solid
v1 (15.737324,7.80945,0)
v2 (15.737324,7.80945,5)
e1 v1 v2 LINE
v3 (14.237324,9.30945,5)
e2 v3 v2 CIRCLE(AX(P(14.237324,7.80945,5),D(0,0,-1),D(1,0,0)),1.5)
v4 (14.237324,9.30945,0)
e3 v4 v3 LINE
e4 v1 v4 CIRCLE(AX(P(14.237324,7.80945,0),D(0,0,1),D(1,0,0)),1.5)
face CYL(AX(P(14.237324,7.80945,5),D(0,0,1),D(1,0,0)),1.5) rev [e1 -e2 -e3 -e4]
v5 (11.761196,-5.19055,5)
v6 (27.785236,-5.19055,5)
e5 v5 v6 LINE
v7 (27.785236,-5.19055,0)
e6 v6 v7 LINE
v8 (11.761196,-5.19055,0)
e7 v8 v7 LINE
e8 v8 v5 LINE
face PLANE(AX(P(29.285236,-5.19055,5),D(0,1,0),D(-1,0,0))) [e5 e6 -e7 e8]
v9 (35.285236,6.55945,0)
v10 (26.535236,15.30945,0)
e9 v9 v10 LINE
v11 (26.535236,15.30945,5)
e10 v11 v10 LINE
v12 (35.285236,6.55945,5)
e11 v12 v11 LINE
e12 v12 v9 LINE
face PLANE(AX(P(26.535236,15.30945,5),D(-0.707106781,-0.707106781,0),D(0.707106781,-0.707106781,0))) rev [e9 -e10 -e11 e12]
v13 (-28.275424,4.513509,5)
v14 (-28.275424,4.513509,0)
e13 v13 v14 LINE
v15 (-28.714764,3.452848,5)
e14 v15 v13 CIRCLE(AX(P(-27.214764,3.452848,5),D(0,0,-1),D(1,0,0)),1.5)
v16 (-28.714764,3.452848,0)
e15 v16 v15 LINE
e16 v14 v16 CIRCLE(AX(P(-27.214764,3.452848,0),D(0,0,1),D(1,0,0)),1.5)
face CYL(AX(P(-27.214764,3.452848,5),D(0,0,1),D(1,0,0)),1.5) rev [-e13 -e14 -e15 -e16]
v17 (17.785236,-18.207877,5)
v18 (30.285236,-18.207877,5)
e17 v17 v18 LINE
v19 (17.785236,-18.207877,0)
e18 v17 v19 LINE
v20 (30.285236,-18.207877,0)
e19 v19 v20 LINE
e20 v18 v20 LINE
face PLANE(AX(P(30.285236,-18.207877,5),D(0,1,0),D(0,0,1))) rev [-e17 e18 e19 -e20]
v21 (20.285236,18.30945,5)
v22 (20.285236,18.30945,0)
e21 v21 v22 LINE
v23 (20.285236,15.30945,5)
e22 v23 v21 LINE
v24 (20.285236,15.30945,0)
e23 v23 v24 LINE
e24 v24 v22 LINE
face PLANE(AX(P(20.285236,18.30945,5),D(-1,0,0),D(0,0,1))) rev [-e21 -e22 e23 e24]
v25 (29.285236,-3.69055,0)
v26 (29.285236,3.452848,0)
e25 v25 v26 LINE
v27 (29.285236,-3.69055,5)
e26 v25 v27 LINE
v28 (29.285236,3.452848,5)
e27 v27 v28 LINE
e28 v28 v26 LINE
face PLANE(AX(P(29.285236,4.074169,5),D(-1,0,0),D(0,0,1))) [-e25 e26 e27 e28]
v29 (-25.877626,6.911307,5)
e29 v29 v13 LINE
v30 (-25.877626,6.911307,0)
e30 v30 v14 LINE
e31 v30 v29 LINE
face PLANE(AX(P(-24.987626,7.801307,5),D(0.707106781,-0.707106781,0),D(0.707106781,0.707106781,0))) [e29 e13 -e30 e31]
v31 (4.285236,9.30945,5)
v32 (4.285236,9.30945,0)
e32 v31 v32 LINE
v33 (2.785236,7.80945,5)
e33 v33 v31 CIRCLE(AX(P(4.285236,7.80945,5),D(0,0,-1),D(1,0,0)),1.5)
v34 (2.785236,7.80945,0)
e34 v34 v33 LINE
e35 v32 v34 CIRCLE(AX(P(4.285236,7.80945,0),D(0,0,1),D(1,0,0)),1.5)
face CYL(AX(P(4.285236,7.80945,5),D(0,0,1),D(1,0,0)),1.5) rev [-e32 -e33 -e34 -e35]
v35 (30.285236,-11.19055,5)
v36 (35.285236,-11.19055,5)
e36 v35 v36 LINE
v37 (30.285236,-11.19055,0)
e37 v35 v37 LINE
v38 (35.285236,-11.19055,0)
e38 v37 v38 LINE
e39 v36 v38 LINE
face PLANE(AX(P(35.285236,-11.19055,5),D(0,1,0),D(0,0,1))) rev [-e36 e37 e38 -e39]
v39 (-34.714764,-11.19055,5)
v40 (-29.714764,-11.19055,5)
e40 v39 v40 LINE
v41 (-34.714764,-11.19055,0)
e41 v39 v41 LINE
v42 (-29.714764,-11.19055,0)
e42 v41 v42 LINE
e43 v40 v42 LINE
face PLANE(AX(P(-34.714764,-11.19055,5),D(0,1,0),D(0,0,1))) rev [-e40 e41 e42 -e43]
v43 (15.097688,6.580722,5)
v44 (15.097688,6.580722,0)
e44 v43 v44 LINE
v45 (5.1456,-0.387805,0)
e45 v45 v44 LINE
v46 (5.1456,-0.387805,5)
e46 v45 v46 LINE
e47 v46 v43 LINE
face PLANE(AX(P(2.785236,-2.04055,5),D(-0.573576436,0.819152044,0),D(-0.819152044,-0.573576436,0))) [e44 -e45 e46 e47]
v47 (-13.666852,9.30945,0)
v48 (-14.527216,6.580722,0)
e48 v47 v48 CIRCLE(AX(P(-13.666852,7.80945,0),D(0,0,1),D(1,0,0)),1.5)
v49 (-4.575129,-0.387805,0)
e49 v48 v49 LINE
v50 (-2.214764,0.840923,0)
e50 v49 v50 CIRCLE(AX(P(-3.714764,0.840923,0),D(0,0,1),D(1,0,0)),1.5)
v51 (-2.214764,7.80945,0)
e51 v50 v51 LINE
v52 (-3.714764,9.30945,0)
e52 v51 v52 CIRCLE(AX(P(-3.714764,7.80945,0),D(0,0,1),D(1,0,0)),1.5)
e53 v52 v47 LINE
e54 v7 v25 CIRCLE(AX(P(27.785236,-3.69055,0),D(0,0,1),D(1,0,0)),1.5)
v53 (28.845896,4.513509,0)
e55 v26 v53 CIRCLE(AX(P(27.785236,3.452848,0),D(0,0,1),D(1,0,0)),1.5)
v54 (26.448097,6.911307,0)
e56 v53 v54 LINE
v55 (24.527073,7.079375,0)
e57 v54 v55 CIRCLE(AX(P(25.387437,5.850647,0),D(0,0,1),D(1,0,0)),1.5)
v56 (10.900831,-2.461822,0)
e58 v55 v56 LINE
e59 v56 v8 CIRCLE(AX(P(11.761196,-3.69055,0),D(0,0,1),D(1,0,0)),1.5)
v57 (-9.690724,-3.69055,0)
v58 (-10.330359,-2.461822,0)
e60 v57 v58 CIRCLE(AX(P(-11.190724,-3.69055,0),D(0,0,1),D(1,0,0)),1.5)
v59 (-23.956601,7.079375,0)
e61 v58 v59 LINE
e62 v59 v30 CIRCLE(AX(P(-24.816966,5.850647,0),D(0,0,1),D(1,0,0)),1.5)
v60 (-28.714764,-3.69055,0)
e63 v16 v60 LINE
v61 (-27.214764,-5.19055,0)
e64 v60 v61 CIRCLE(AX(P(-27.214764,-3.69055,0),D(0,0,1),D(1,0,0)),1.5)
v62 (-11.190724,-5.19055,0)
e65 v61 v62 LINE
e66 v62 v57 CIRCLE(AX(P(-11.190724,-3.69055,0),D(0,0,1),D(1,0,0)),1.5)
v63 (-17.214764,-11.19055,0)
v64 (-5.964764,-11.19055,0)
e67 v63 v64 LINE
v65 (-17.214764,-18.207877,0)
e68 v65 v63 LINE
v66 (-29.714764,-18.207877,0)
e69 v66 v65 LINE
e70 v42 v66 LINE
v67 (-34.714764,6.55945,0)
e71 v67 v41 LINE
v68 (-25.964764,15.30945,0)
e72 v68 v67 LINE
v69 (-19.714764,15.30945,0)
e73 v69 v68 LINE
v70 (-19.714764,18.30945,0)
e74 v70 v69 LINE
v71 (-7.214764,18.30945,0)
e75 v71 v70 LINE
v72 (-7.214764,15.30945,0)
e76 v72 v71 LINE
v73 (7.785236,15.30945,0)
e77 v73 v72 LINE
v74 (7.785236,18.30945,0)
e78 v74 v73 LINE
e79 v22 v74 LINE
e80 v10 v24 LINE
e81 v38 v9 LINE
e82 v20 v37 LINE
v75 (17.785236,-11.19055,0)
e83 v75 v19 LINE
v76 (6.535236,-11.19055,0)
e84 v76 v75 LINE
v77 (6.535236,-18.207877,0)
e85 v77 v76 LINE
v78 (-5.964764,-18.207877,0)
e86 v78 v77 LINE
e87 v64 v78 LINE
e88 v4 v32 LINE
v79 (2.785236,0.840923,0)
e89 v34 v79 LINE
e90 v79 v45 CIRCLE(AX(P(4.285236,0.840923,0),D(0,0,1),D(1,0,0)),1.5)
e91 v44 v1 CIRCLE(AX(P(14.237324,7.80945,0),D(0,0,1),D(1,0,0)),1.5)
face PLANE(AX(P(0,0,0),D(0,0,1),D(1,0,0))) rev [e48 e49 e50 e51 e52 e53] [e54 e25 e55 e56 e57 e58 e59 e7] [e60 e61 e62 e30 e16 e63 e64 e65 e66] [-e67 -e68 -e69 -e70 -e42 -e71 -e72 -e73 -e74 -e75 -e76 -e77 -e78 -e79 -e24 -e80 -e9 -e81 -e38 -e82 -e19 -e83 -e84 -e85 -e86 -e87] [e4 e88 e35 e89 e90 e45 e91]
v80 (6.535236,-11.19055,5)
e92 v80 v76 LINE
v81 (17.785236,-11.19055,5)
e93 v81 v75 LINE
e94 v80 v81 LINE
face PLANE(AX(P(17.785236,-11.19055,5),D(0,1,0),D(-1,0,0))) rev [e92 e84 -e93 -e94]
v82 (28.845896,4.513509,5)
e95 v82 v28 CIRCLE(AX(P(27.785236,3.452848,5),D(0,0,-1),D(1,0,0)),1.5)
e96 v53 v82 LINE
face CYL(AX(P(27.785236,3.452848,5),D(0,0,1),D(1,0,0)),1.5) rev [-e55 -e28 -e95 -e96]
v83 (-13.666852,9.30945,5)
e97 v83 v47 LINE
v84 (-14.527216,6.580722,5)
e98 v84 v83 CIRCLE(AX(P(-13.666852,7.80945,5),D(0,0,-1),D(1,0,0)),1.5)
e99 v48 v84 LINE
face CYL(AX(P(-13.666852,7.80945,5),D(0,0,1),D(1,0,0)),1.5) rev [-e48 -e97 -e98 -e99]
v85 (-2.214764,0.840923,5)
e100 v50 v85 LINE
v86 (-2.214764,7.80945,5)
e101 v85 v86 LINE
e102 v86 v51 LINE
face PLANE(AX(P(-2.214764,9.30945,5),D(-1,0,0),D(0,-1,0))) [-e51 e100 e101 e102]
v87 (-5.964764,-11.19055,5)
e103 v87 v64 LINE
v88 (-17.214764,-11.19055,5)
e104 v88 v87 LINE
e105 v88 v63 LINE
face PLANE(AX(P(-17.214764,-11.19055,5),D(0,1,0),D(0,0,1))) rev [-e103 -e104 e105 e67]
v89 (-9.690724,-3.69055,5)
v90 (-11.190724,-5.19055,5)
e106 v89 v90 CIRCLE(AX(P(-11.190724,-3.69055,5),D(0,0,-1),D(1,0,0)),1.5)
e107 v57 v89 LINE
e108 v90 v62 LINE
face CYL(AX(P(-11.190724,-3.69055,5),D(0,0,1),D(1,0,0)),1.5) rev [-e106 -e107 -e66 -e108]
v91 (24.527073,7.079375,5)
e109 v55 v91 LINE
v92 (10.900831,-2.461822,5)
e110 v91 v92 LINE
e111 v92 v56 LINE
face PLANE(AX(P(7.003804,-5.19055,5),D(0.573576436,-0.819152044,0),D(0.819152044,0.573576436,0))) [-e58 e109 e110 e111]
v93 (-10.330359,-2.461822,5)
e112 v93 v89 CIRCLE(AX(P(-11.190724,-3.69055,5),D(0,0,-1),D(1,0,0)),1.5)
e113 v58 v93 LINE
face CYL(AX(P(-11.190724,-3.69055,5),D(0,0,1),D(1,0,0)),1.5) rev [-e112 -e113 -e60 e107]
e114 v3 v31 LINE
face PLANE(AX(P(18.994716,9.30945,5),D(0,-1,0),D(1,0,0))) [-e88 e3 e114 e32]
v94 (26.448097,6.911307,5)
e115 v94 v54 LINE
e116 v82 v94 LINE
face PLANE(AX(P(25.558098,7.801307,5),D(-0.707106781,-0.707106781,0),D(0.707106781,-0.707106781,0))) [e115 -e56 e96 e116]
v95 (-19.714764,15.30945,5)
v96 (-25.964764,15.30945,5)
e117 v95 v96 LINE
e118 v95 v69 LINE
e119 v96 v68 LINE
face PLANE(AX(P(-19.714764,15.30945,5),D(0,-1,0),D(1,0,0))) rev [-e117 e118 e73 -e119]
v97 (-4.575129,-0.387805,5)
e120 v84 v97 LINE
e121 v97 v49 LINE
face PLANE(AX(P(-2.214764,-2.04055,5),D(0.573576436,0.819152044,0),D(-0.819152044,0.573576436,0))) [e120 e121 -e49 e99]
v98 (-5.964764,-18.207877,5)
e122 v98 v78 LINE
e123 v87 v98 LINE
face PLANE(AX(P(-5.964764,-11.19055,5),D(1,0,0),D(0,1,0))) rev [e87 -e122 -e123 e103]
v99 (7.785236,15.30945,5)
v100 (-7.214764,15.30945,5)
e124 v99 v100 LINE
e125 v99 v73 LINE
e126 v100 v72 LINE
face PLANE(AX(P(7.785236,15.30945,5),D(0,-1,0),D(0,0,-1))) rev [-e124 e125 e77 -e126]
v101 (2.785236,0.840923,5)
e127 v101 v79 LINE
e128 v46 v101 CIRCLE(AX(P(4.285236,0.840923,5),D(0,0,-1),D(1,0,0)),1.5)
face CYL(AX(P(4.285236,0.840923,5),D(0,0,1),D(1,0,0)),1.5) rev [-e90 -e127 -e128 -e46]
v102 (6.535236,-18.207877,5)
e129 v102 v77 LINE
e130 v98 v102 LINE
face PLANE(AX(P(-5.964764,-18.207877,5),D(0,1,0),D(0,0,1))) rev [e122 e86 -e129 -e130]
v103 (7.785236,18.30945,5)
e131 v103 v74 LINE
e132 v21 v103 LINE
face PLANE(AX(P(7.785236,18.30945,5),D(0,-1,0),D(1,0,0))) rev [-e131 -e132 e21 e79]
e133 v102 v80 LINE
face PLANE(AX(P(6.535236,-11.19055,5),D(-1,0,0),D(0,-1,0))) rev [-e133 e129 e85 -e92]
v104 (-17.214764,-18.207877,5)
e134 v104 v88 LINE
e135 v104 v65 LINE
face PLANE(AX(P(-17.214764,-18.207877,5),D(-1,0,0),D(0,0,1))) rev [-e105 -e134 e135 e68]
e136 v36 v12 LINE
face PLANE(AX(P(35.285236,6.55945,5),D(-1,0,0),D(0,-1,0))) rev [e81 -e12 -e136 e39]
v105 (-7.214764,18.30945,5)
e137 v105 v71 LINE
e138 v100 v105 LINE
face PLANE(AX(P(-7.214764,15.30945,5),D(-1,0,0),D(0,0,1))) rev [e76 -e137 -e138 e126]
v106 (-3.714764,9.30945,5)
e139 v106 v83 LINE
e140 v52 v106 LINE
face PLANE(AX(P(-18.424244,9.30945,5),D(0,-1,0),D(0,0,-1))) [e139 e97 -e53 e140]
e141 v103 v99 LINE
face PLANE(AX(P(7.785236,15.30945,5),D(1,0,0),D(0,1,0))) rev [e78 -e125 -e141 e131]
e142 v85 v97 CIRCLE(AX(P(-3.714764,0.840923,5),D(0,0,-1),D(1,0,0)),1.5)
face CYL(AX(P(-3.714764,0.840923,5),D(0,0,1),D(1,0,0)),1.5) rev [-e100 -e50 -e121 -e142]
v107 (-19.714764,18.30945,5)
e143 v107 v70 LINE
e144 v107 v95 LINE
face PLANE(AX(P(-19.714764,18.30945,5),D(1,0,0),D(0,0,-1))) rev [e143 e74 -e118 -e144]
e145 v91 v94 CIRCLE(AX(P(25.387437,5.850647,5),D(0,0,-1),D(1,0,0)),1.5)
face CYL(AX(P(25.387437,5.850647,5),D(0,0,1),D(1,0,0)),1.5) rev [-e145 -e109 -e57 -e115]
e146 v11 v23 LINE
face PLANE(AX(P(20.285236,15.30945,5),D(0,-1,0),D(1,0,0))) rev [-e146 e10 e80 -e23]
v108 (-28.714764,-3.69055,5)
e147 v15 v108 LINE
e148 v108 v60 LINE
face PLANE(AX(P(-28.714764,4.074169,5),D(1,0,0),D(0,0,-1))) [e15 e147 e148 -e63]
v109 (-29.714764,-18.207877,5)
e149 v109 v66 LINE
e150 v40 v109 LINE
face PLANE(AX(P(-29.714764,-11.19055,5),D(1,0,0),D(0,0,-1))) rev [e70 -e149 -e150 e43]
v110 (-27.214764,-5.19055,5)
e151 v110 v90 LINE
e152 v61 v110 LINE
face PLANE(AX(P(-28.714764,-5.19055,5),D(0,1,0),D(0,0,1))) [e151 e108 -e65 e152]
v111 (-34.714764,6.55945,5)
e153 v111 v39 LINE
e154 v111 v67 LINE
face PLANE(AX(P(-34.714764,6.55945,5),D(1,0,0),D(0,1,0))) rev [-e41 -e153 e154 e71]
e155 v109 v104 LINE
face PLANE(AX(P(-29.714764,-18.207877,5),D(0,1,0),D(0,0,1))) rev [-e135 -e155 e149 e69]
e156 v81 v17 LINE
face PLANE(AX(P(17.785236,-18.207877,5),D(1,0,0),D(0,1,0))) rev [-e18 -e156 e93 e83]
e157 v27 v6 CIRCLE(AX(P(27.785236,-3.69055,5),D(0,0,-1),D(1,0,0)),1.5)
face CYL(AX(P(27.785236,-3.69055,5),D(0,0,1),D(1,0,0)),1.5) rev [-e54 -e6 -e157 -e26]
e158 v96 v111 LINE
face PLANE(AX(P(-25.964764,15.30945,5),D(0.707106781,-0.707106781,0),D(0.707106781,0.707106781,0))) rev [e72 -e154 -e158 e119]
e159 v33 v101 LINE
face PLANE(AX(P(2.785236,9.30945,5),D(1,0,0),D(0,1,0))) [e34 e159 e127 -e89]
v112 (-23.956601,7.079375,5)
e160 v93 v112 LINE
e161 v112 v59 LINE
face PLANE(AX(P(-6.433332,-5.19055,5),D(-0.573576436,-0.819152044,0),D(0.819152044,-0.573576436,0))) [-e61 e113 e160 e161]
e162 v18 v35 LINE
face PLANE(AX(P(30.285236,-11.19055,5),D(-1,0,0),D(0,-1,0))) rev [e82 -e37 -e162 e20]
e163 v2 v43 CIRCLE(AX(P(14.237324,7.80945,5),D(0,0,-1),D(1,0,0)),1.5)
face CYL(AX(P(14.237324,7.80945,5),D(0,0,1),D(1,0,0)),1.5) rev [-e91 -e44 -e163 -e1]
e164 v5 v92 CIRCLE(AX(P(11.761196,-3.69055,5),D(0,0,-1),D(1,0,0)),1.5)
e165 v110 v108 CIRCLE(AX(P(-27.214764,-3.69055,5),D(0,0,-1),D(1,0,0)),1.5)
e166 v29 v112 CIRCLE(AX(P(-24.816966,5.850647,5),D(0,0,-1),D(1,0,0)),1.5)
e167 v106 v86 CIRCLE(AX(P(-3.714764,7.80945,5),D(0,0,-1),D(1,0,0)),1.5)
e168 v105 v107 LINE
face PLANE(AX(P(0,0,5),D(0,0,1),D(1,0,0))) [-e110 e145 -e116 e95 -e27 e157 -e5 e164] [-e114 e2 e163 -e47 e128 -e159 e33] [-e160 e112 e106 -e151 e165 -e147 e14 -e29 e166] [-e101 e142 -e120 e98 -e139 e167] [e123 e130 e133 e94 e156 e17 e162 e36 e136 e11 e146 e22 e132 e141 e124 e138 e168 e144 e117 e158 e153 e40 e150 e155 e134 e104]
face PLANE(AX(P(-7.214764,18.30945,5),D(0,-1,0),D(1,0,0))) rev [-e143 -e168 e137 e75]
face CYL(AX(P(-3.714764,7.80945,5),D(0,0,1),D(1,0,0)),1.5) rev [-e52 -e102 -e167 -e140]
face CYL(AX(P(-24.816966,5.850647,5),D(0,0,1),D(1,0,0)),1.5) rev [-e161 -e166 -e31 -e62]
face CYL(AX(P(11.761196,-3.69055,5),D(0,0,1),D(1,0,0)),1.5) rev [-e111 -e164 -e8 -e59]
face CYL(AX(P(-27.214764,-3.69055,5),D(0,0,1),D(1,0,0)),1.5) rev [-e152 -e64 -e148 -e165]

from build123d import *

# Parameters (mm, degrees)
EXTRUDE_1_DEPTH = 5
FILLET_3_R      = 1.5
FILLET_4_R      = 1.5
FILLET_5_R      = 1.5


with BuildPart() as part:
    # 草图1 → 凸台-拉伸1 (new body)
    with BuildSketch(Plane.XY):
        Polygon((7.785235828, 15.309450129), (-7.214764172, 15.309450129), (-7.214764172, 18.309450129), (-19.714764172, 18.309450129), (-19.714764172, 15.309450129), (-25.964764172, 15.309450129), (-34.714764172, 6.559450129), (-34.714764172, -11.190549871), (-29.714764172, -11.190549871), (-29.714764172, -18.207876603), (-17.214764172, -18.207876603), (-17.214764172, -11.190549871), (-5.964764172, -11.190549871), (-5.964764172, -18.207876603), (6.535235828, -18.207876603), (6.535235828, -11.190549871), (17.785235828, -11.190549871), (17.785235828, -18.207876603), (30.285235828, -18.207876603), (30.285235828, -11.190549871), (35.285235828, -11.190549871), (35.285235828, 6.559450129), (26.535235828, 15.309450129), (20.285235828, 15.309450129), (20.285235828, 18.309450129), (7.785235828, 18.309450129), align=None)
        Polygon((-24.987626131, 7.801306796), (-28.714764172, 4.074168755), (-28.714764172, -5.190549871), (-6.433331929, -5.190549871), align=None, mode=Mode.SUBTRACT)
        Polygon((-18.424244048, 9.309450129), (-2.214764172, 9.309450129), (-2.214764172, -2.040549871), align=None, mode=Mode.SUBTRACT)
        Polygon((2.785235828, -2.040549871), (18.994715705, 9.309450129), (2.785235828, 9.309450129), align=None, mode=Mode.SUBTRACT)
        Polygon((7.003803585, -5.190549871), (25.558097787, 7.801306796), (29.285235828, 4.074168755), (29.285235828, -5.190549871), align=None, mode=Mode.SUBTRACT)
    extrude(amount=EXTRUDE_1_DEPTH)

    # 圆角3
    fillet_3_edges = [part.edges().sort_by_distance(p)[0] for p in [
        (-24.987626131, 7.801306796, 2.5),
    ]]
    fillet(fillet_3_edges, radius=FILLET_3_R)

    # 圆角4
    fillet_4_edges = [part.edges().sort_by_distance(p)[0] for p in [
        (-6.433331929, -5.190549871, 2.5),
        (-28.714764172, 4.074168755, 2.5),
        (-28.714764172, -5.190549871, 2.5),
    ]]
    fillet(fillet_4_edges, radius=FILLET_4_R)

    # 圆角5
    fillet_5_edges = [part.edges().sort_by_distance(p)[0] for p in [
        (29.285235828, -5.190549871, 2.5),
        (29.285235828, 4.074168755, 2.5),
        (25.558097787, 7.801306796, 2.5),
        (-18.424244048, 9.309450129, 2.5),
        (-2.214764172, -2.040549871, 2.5),
        (-2.214764172, 9.309450129, 2.5),
        (2.785235828, 9.309450129, 2.5),
        (2.785235828, -2.040549871, 2.5),
        (18.994715705, 9.309450129, 2.5),
        (7.003803585, -5.190549871, 2.5),
    ]]
    fillet(fillet_5_edges, radius=FILLET_5_R)


solid = part.part
